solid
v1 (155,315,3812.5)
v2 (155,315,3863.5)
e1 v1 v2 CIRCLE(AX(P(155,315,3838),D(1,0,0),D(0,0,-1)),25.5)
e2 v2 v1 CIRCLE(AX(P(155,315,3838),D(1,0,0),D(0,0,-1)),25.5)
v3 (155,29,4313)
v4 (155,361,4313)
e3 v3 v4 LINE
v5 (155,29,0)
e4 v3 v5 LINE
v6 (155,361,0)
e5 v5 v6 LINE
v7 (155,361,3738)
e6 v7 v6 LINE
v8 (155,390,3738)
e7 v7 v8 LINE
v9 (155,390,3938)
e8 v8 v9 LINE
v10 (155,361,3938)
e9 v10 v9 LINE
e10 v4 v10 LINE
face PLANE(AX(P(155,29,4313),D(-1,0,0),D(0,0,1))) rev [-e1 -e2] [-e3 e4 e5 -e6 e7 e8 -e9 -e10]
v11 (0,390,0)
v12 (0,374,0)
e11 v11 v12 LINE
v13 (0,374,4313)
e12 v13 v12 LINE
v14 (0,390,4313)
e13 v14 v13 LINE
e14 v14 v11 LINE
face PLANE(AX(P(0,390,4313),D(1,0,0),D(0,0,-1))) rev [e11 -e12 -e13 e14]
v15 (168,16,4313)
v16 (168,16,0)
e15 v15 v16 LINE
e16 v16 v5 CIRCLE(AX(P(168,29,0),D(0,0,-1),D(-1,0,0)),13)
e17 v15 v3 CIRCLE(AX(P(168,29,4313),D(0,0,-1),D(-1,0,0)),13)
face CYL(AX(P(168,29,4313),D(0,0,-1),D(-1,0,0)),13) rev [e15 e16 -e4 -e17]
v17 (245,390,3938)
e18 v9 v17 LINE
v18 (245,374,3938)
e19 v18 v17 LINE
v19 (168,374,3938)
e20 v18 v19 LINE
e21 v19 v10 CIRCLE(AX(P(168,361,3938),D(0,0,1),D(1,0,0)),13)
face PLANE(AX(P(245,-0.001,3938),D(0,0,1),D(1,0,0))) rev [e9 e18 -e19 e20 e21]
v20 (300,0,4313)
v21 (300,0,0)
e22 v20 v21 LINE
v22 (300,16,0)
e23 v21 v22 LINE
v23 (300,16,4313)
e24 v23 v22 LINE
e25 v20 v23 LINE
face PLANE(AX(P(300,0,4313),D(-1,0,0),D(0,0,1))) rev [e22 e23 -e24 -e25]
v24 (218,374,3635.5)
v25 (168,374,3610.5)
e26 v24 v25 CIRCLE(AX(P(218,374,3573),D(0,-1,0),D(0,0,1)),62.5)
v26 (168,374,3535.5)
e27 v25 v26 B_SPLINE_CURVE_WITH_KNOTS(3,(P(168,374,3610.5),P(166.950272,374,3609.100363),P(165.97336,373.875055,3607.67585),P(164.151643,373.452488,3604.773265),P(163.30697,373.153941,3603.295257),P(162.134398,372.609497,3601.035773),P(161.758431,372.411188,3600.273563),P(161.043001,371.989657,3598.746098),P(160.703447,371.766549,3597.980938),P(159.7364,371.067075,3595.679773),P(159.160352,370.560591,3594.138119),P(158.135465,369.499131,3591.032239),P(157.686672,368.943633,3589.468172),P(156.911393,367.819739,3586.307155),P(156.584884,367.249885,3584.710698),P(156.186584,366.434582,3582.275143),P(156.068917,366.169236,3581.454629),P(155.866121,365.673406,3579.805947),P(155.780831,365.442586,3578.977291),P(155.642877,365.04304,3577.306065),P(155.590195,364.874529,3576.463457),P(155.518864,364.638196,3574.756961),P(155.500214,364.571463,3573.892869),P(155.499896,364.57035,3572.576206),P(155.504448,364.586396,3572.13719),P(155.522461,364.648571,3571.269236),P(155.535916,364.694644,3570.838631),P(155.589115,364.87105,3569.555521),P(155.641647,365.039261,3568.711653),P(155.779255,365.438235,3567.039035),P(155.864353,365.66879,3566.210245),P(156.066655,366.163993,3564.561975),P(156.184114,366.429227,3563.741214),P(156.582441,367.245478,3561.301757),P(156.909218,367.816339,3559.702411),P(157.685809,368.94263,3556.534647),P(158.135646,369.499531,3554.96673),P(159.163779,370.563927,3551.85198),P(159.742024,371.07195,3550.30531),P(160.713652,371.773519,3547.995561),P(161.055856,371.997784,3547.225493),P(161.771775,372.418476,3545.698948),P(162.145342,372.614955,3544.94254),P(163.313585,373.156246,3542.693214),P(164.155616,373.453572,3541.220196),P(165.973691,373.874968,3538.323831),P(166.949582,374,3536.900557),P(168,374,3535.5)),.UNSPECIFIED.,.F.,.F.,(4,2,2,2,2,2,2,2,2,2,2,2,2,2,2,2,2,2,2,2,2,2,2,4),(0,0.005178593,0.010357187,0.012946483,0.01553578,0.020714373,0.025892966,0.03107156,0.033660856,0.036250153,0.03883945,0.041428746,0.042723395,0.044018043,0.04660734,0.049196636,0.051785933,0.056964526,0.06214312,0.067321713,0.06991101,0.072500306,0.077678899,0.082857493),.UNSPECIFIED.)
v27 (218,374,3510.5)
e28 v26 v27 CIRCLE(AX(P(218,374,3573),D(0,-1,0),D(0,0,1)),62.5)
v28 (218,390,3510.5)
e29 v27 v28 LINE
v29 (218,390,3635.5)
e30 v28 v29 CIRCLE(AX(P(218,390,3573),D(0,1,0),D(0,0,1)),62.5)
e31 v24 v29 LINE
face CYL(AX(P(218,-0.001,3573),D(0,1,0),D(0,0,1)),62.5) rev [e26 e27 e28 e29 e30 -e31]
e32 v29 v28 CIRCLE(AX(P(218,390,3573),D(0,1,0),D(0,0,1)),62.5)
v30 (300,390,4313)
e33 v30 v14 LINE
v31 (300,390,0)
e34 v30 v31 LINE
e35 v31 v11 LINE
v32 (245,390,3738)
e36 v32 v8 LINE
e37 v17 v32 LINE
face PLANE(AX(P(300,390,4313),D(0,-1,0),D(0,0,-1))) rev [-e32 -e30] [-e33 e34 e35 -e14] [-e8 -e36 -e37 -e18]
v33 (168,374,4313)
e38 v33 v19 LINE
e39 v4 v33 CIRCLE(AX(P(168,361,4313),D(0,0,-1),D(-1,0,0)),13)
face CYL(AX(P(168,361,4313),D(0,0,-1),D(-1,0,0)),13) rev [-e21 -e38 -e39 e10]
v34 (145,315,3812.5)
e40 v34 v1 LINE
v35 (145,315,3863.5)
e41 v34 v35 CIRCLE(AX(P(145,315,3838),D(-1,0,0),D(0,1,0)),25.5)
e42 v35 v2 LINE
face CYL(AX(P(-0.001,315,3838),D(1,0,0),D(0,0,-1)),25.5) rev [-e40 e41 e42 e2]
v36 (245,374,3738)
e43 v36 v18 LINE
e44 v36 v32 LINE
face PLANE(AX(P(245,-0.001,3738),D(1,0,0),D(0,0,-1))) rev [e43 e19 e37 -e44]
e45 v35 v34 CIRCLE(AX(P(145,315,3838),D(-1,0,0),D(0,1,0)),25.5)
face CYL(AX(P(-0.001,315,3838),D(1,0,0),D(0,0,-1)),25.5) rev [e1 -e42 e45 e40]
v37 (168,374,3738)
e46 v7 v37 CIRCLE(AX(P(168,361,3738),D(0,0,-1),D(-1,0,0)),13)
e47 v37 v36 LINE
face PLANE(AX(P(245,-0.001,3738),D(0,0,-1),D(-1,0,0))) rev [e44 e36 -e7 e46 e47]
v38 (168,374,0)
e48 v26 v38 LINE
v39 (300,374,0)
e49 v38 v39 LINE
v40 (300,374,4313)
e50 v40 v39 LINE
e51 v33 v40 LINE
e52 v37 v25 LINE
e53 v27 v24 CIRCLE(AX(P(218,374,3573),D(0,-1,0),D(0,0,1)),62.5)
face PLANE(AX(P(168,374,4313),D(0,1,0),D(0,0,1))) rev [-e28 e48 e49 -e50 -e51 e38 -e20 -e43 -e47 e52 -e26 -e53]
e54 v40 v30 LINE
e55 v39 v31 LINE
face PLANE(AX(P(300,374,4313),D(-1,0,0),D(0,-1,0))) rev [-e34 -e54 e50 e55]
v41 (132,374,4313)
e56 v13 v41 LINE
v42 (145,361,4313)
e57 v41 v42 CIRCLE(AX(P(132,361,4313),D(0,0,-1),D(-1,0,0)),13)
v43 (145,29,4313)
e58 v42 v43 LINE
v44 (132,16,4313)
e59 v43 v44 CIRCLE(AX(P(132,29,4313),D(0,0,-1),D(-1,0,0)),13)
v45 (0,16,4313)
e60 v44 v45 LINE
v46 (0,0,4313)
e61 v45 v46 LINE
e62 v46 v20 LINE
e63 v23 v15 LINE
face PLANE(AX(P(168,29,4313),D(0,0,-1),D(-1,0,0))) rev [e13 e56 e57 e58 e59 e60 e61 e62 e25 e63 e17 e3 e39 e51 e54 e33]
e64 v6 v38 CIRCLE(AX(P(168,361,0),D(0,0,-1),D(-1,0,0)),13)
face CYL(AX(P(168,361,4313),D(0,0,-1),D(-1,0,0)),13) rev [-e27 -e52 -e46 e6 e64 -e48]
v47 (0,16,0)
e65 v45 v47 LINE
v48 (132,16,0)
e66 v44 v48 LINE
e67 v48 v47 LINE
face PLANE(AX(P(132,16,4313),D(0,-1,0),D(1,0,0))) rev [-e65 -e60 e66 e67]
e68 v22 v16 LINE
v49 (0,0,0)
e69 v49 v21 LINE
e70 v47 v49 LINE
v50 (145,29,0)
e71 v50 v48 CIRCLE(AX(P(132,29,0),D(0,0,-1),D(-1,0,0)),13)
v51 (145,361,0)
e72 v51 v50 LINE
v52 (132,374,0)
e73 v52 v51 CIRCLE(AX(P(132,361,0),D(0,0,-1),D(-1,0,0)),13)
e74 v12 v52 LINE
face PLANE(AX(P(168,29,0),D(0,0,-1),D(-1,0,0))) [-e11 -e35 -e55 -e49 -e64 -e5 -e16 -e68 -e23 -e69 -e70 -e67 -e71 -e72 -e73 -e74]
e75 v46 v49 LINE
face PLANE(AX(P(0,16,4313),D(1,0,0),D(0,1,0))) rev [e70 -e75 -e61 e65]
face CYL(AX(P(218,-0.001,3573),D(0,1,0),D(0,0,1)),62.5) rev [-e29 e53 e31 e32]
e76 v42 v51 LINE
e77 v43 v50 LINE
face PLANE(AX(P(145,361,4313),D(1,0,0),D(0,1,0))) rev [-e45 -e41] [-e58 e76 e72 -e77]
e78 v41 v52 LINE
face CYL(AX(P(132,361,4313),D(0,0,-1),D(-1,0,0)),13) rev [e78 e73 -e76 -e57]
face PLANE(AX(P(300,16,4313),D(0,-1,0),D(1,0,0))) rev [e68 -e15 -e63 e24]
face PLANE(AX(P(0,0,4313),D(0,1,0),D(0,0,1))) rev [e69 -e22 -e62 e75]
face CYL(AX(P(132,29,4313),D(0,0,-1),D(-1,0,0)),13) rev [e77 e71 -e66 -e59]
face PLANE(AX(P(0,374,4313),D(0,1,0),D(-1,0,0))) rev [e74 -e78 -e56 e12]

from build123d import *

# Parameters (mm, degrees)
BOSS_EXTRUDE1_DEPTH = 4313
CUT_EXTRUDE1_REACH  = 4342.976
SKETCH2_R           = 62.5
SKETCH2_W           = 90
SKETCH2_H           = 200
CUT_EXTRUDE2_REACH  = 4335.37
SKETCH3_R           = 25.5


with BuildPart() as part:
    # Sketch1 → Boss-Extrude1 (new body)
    with BuildSketch(Plane.XY):
        with BuildLine():
            Line((0, 0), (300, 0))
            Line((300, 0), (300, 16))
            Line((300, 16), (168, 16))
            ThreePointArc((168, 16), (158.807611845, 19.807611845), (155, 29))
            Line((155, 29), (155, 361))
            ThreePointArc((155, 361), (158.807611845, 370.192388155), (168, 374))
            Line((168, 374), (300, 374))
            Line((300, 374), (300, 390))
            Line((300, 390), (0, 390))
            Line((0, 390), (0, 374))
            Line((0, 374), (132, 374))
            ThreePointArc((132, 374), (141.192388155, 370.192388155), (145, 361))
            Line((145, 361), (145, 29))
            ThreePointArc((145, 29), (141.192388155, 19.807611845), (132, 16))
            Line((132, 16), (0, 16))
            Line((0, 16), (0, 0))
        make_face()
    extrude(amount=BOSS_EXTRUDE1_DEPTH)

    # Sketch2 → Cut-Extrude1 (cut, up to next)
    with BuildSketch(Plane(origin=(0, 390, 0), x_dir=(1, 0, 0), z_dir=(0, 1, 0)), mode=Mode.PRIVATE) as cut_extrude1_sk1:
        with Locations(Location((218, -3573, 0), (0, 0, 270))):
            Circle(SKETCH2_R)
    cut_extrude1_tool1 = extrude(cut_extrude1_sk1.sketch, amount=-CUT_EXTRUDE1_REACH, mode=Mode.PRIVATE) & part.part
    # Sketch2 → Cut-Extrude1 (cut, up to next)
    with BuildSketch(Plane(origin=(0, 390, 0), x_dir=(1, 0, 0), z_dir=(0, 1, 0)), mode=Mode.PRIVATE) as cut_extrude1_sk2:
        with Locations((200, -3838)):
            Rectangle(SKETCH2_W, SKETCH2_H)
    cut_extrude1_tool2 = extrude(cut_extrude1_sk2.sketch, amount=-CUT_EXTRUDE1_REACH, mode=Mode.PRIVATE) & part.part
    add(cut_extrude1_tool1.solids().sort_by_distance((218, 390, 3573))[0], mode=Mode.SUBTRACT)
    add(cut_extrude1_tool2.solids().sort_by_distance((200, 390, 3838))[0], mode=Mode.SUBTRACT)

    # Sketch3 → Cut-Extrude2 (cut, up to next)
    with BuildSketch(Plane(origin=(155, 0, 0), x_dir=(0, 0, -1), z_dir=(1, 0, 0)), mode=Mode.PRIVATE) as cut_extrude2_sk1:
        with Locations((-3838, 315)):
            Circle(SKETCH3_R)
    cut_extrude2_tool1 = extrude(cut_extrude2_sk1.sketch, amount=-CUT_EXTRUDE2_REACH, mode=Mode.PRIVATE) & part.part
    add(cut_extrude2_tool1.solids().sort_by_distance((155, 315, 3838))[0], mode=Mode.SUBTRACT)


solid = part.part
